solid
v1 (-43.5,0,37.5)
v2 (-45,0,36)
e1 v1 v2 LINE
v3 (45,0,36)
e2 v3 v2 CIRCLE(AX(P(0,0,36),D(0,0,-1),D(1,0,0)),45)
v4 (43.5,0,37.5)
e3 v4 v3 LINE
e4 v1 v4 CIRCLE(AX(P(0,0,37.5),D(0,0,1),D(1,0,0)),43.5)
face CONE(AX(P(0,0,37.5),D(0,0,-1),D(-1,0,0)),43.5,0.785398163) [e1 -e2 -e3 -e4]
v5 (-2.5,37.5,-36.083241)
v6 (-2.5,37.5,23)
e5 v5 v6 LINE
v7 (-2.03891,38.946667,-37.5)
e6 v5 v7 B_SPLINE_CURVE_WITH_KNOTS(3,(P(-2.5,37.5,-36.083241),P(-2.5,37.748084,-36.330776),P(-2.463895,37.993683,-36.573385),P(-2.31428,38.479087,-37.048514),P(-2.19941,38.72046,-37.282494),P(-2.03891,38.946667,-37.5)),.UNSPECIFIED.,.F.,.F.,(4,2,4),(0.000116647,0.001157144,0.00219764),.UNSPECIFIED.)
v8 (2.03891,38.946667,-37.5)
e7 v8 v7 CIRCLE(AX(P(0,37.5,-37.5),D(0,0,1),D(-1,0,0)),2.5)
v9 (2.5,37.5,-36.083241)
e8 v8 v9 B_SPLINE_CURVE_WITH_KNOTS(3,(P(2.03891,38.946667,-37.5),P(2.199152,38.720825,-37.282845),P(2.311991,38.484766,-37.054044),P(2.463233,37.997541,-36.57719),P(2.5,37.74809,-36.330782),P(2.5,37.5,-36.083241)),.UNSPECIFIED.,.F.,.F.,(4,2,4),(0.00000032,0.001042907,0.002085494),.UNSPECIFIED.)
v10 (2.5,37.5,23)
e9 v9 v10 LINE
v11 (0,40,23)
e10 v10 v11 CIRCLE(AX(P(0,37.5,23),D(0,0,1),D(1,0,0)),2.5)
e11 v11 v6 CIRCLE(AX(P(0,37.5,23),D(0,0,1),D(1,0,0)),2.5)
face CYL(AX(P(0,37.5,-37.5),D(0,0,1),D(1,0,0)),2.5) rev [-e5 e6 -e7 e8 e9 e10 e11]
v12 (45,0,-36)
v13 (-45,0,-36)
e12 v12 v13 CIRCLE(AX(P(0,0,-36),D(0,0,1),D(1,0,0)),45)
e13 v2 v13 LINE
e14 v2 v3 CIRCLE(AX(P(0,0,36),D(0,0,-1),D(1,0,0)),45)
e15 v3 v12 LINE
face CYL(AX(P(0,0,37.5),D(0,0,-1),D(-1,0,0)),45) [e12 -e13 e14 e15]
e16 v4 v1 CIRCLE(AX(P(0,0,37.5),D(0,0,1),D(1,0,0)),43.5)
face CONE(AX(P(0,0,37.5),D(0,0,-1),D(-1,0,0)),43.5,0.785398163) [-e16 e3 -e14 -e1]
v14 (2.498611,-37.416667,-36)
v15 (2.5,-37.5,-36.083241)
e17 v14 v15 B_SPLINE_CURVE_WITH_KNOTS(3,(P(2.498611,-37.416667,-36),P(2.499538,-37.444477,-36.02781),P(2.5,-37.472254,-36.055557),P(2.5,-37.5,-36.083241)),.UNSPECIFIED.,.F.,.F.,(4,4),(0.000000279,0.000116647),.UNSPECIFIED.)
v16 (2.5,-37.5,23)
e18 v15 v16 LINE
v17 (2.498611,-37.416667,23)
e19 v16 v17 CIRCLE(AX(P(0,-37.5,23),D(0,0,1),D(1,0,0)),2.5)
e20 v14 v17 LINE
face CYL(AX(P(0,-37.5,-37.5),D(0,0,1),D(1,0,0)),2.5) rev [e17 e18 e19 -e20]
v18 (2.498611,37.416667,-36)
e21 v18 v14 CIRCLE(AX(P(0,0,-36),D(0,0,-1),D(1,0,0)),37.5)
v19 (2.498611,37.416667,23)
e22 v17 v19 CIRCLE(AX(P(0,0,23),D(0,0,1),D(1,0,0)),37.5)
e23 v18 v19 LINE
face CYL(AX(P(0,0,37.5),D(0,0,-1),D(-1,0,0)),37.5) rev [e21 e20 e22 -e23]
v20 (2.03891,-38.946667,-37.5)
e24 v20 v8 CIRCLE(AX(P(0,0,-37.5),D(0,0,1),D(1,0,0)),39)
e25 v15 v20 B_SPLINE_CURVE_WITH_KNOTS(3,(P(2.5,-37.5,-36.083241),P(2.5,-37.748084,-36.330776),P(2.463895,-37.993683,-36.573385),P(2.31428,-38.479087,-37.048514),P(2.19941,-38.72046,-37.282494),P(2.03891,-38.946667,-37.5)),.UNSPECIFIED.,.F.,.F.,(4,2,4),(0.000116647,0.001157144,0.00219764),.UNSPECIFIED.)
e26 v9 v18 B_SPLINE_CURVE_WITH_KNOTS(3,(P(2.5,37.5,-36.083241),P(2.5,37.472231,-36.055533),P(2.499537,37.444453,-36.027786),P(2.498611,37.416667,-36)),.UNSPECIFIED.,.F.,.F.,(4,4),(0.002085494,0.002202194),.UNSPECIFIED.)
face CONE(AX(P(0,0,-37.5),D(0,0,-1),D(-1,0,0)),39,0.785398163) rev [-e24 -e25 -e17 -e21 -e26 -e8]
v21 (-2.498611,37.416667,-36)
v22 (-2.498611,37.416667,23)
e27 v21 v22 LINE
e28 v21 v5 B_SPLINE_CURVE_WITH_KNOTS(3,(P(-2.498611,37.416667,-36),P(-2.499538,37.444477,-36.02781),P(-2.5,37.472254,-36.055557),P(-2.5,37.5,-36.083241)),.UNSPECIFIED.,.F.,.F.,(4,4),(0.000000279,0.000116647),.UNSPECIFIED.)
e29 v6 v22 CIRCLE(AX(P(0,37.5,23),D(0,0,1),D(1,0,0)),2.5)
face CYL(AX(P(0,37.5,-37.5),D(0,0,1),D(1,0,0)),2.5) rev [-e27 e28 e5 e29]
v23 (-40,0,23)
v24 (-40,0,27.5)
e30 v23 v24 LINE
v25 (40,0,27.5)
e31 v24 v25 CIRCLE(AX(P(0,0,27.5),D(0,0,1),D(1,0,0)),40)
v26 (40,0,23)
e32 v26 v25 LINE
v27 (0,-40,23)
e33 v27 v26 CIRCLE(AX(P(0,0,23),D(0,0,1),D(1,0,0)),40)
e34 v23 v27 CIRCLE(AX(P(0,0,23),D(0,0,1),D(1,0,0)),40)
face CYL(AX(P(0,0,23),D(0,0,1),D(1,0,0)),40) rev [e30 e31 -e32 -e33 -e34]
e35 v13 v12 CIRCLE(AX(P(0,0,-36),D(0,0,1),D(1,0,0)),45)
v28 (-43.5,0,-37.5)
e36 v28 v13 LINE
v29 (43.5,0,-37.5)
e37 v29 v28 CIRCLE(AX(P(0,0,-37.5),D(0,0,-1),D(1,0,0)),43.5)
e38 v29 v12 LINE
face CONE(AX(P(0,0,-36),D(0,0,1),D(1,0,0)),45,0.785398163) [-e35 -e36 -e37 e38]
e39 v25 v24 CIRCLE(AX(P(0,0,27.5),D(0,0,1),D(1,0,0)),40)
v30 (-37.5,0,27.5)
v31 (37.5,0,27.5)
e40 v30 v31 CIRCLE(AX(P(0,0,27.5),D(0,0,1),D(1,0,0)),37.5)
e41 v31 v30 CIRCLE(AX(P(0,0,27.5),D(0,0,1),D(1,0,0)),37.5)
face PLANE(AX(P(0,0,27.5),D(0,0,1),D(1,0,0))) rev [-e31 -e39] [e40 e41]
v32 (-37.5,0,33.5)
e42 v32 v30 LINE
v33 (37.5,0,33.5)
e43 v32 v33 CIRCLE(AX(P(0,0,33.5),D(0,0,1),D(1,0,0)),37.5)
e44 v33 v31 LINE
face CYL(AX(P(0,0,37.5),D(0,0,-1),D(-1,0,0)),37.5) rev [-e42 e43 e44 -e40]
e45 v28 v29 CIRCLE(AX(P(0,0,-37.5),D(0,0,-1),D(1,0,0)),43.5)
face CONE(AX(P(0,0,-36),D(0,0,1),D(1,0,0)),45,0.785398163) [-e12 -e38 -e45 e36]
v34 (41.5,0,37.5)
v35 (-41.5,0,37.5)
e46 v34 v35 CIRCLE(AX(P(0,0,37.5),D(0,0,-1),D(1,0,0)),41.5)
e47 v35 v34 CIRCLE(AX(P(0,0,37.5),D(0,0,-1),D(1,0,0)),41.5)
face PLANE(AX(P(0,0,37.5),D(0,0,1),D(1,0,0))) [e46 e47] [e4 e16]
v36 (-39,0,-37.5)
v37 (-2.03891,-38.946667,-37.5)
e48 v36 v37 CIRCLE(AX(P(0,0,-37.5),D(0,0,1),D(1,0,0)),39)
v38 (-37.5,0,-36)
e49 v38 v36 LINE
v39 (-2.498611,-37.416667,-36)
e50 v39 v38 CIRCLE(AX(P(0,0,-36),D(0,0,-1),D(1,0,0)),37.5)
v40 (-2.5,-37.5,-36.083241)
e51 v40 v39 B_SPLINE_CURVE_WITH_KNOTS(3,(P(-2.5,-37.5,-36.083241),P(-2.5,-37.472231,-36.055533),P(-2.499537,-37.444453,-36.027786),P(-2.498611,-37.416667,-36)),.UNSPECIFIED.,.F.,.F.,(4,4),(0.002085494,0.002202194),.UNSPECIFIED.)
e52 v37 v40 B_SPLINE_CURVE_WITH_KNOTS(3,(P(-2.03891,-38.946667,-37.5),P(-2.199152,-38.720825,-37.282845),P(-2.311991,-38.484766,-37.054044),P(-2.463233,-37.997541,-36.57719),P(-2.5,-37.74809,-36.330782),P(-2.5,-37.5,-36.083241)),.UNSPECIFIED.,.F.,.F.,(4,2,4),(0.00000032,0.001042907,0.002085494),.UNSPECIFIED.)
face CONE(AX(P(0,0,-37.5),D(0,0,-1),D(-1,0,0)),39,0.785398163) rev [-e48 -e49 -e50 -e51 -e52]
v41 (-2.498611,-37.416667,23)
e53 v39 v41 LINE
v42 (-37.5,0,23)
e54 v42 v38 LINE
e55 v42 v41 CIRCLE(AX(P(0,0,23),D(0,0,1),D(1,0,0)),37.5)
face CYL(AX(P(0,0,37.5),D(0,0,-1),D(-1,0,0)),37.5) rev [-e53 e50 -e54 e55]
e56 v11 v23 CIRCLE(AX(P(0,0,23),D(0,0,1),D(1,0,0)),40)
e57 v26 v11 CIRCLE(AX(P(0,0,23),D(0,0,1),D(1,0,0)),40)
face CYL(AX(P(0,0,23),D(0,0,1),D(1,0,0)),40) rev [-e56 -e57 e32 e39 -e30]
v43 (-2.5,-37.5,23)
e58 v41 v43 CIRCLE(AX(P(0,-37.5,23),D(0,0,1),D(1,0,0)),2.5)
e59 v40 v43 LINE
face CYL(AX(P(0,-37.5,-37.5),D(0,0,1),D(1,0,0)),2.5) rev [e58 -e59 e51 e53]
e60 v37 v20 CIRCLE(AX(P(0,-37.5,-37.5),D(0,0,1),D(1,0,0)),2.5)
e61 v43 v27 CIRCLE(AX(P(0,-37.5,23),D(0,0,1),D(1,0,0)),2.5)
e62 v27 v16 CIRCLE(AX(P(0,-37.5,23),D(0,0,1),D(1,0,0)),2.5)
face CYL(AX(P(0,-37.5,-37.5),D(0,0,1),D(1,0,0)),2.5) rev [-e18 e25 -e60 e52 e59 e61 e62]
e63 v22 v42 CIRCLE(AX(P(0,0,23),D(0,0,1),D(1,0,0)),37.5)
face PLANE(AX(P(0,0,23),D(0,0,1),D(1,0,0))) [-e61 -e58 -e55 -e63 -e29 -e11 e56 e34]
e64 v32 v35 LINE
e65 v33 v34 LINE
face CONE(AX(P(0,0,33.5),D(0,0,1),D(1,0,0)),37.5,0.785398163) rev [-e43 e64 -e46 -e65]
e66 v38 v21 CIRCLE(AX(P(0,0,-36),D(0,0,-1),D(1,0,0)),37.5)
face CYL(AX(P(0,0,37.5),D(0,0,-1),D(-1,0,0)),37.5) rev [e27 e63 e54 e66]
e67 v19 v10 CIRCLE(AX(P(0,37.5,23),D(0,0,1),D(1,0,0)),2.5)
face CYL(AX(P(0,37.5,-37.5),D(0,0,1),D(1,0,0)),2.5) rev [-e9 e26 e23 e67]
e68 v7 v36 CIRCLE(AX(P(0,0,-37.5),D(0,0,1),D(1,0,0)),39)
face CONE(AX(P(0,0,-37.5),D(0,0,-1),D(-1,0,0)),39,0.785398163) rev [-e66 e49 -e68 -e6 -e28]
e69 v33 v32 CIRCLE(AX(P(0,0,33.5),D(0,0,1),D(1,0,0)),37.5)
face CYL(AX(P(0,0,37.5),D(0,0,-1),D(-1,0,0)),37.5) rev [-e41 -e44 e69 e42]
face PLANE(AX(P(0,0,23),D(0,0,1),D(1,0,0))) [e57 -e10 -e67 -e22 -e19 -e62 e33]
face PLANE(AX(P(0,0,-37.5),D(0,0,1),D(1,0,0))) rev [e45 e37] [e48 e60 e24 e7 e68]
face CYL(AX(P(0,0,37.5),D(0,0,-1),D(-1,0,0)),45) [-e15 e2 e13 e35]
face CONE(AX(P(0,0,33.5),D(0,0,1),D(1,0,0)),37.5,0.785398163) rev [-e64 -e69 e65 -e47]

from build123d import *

# Parameters (mm, degrees)
SKETCH1_R           = 45
SKETCH1_R_2         = 37.5
BOSS_EXTRUDE1_DEPTH = 37.5
CUT_EXTRUDE1_START  = -4.5
SKETCH2_R           = 40
SKETCH2_R_2         = 37.5
CUT_EXTRUDE1_DEPTH  = 4.5
CHAMFERC1_5_SIZE    = 1.5
CHAMFERC4_SIZE      = 4
CUT_EXTRUDE2_DEPTH  = 91.967026993


with BuildPart() as part:
    # Sketch1 → Boss-Extrude1 (new, symmetric)
    with BuildSketch(Plane.XY):
        Circle(SKETCH1_R)
        Circle(SKETCH1_R_2, mode=Mode.SUBTRACT)
    extrude(amount=BOSS_EXTRUDE1_DEPTH, both=True)

    # Sketch2 → Cut-Extrude1 (cut)
    with BuildSketch(Plane.XY.offset(27.5).offset(CUT_EXTRUDE1_START)):
        Circle(SKETCH2_R)
        Circle(SKETCH2_R_2, mode=Mode.SUBTRACT)
    extrude(amount=CUT_EXTRUDE1_DEPTH, mode=Mode.SUBTRACT)

    # ChamferC1.5
    chamferc1_5_edges = [part.edges().sort_by_distance(p)[0] for p in [
        (-45, 0, -37.5),
        (-45, 0, 37.5),
        (-37.5, 0, -37.5),
    ]]
    chamfer(chamferc1_5_edges, length=CHAMFERC1_5_SIZE)

    # ChamferC4
    chamferc4_edges = [part.edges().sort_by_distance(p)[0] for p in [
        (-37.5, 0, 37.5),
    ]]
    chamfer(chamferc4_edges, length=CHAMFERC4_SIZE)

    # Sketch3 → Cut-Extrude2 (cut, through all)
    with BuildSketch(Plane.XY.offset(27.5)):
        with BuildLine():
            ThreePointArc((2.498610725, 37.416666667), (0, 37.5), (-2.498610725, 37.416666667))
            ThreePointArc((-2.498610725, 37.416666667), (0, 40), (2.498610725, 37.416666667))
        make_face()
        with BuildLine():
            ThreePointArc((-2.498610725, -37.416666667), (0, -40), (2.498610725, -37.416666667))
            ThreePointArc((2.498610725, -37.416666667), (0, -37.5), (-2.498610725, -37.416666667))
        make_face()
    extrude(amount=-CUT_EXTRUDE2_DEPTH, mode=Mode.SUBTRACT)


solid = part.part
